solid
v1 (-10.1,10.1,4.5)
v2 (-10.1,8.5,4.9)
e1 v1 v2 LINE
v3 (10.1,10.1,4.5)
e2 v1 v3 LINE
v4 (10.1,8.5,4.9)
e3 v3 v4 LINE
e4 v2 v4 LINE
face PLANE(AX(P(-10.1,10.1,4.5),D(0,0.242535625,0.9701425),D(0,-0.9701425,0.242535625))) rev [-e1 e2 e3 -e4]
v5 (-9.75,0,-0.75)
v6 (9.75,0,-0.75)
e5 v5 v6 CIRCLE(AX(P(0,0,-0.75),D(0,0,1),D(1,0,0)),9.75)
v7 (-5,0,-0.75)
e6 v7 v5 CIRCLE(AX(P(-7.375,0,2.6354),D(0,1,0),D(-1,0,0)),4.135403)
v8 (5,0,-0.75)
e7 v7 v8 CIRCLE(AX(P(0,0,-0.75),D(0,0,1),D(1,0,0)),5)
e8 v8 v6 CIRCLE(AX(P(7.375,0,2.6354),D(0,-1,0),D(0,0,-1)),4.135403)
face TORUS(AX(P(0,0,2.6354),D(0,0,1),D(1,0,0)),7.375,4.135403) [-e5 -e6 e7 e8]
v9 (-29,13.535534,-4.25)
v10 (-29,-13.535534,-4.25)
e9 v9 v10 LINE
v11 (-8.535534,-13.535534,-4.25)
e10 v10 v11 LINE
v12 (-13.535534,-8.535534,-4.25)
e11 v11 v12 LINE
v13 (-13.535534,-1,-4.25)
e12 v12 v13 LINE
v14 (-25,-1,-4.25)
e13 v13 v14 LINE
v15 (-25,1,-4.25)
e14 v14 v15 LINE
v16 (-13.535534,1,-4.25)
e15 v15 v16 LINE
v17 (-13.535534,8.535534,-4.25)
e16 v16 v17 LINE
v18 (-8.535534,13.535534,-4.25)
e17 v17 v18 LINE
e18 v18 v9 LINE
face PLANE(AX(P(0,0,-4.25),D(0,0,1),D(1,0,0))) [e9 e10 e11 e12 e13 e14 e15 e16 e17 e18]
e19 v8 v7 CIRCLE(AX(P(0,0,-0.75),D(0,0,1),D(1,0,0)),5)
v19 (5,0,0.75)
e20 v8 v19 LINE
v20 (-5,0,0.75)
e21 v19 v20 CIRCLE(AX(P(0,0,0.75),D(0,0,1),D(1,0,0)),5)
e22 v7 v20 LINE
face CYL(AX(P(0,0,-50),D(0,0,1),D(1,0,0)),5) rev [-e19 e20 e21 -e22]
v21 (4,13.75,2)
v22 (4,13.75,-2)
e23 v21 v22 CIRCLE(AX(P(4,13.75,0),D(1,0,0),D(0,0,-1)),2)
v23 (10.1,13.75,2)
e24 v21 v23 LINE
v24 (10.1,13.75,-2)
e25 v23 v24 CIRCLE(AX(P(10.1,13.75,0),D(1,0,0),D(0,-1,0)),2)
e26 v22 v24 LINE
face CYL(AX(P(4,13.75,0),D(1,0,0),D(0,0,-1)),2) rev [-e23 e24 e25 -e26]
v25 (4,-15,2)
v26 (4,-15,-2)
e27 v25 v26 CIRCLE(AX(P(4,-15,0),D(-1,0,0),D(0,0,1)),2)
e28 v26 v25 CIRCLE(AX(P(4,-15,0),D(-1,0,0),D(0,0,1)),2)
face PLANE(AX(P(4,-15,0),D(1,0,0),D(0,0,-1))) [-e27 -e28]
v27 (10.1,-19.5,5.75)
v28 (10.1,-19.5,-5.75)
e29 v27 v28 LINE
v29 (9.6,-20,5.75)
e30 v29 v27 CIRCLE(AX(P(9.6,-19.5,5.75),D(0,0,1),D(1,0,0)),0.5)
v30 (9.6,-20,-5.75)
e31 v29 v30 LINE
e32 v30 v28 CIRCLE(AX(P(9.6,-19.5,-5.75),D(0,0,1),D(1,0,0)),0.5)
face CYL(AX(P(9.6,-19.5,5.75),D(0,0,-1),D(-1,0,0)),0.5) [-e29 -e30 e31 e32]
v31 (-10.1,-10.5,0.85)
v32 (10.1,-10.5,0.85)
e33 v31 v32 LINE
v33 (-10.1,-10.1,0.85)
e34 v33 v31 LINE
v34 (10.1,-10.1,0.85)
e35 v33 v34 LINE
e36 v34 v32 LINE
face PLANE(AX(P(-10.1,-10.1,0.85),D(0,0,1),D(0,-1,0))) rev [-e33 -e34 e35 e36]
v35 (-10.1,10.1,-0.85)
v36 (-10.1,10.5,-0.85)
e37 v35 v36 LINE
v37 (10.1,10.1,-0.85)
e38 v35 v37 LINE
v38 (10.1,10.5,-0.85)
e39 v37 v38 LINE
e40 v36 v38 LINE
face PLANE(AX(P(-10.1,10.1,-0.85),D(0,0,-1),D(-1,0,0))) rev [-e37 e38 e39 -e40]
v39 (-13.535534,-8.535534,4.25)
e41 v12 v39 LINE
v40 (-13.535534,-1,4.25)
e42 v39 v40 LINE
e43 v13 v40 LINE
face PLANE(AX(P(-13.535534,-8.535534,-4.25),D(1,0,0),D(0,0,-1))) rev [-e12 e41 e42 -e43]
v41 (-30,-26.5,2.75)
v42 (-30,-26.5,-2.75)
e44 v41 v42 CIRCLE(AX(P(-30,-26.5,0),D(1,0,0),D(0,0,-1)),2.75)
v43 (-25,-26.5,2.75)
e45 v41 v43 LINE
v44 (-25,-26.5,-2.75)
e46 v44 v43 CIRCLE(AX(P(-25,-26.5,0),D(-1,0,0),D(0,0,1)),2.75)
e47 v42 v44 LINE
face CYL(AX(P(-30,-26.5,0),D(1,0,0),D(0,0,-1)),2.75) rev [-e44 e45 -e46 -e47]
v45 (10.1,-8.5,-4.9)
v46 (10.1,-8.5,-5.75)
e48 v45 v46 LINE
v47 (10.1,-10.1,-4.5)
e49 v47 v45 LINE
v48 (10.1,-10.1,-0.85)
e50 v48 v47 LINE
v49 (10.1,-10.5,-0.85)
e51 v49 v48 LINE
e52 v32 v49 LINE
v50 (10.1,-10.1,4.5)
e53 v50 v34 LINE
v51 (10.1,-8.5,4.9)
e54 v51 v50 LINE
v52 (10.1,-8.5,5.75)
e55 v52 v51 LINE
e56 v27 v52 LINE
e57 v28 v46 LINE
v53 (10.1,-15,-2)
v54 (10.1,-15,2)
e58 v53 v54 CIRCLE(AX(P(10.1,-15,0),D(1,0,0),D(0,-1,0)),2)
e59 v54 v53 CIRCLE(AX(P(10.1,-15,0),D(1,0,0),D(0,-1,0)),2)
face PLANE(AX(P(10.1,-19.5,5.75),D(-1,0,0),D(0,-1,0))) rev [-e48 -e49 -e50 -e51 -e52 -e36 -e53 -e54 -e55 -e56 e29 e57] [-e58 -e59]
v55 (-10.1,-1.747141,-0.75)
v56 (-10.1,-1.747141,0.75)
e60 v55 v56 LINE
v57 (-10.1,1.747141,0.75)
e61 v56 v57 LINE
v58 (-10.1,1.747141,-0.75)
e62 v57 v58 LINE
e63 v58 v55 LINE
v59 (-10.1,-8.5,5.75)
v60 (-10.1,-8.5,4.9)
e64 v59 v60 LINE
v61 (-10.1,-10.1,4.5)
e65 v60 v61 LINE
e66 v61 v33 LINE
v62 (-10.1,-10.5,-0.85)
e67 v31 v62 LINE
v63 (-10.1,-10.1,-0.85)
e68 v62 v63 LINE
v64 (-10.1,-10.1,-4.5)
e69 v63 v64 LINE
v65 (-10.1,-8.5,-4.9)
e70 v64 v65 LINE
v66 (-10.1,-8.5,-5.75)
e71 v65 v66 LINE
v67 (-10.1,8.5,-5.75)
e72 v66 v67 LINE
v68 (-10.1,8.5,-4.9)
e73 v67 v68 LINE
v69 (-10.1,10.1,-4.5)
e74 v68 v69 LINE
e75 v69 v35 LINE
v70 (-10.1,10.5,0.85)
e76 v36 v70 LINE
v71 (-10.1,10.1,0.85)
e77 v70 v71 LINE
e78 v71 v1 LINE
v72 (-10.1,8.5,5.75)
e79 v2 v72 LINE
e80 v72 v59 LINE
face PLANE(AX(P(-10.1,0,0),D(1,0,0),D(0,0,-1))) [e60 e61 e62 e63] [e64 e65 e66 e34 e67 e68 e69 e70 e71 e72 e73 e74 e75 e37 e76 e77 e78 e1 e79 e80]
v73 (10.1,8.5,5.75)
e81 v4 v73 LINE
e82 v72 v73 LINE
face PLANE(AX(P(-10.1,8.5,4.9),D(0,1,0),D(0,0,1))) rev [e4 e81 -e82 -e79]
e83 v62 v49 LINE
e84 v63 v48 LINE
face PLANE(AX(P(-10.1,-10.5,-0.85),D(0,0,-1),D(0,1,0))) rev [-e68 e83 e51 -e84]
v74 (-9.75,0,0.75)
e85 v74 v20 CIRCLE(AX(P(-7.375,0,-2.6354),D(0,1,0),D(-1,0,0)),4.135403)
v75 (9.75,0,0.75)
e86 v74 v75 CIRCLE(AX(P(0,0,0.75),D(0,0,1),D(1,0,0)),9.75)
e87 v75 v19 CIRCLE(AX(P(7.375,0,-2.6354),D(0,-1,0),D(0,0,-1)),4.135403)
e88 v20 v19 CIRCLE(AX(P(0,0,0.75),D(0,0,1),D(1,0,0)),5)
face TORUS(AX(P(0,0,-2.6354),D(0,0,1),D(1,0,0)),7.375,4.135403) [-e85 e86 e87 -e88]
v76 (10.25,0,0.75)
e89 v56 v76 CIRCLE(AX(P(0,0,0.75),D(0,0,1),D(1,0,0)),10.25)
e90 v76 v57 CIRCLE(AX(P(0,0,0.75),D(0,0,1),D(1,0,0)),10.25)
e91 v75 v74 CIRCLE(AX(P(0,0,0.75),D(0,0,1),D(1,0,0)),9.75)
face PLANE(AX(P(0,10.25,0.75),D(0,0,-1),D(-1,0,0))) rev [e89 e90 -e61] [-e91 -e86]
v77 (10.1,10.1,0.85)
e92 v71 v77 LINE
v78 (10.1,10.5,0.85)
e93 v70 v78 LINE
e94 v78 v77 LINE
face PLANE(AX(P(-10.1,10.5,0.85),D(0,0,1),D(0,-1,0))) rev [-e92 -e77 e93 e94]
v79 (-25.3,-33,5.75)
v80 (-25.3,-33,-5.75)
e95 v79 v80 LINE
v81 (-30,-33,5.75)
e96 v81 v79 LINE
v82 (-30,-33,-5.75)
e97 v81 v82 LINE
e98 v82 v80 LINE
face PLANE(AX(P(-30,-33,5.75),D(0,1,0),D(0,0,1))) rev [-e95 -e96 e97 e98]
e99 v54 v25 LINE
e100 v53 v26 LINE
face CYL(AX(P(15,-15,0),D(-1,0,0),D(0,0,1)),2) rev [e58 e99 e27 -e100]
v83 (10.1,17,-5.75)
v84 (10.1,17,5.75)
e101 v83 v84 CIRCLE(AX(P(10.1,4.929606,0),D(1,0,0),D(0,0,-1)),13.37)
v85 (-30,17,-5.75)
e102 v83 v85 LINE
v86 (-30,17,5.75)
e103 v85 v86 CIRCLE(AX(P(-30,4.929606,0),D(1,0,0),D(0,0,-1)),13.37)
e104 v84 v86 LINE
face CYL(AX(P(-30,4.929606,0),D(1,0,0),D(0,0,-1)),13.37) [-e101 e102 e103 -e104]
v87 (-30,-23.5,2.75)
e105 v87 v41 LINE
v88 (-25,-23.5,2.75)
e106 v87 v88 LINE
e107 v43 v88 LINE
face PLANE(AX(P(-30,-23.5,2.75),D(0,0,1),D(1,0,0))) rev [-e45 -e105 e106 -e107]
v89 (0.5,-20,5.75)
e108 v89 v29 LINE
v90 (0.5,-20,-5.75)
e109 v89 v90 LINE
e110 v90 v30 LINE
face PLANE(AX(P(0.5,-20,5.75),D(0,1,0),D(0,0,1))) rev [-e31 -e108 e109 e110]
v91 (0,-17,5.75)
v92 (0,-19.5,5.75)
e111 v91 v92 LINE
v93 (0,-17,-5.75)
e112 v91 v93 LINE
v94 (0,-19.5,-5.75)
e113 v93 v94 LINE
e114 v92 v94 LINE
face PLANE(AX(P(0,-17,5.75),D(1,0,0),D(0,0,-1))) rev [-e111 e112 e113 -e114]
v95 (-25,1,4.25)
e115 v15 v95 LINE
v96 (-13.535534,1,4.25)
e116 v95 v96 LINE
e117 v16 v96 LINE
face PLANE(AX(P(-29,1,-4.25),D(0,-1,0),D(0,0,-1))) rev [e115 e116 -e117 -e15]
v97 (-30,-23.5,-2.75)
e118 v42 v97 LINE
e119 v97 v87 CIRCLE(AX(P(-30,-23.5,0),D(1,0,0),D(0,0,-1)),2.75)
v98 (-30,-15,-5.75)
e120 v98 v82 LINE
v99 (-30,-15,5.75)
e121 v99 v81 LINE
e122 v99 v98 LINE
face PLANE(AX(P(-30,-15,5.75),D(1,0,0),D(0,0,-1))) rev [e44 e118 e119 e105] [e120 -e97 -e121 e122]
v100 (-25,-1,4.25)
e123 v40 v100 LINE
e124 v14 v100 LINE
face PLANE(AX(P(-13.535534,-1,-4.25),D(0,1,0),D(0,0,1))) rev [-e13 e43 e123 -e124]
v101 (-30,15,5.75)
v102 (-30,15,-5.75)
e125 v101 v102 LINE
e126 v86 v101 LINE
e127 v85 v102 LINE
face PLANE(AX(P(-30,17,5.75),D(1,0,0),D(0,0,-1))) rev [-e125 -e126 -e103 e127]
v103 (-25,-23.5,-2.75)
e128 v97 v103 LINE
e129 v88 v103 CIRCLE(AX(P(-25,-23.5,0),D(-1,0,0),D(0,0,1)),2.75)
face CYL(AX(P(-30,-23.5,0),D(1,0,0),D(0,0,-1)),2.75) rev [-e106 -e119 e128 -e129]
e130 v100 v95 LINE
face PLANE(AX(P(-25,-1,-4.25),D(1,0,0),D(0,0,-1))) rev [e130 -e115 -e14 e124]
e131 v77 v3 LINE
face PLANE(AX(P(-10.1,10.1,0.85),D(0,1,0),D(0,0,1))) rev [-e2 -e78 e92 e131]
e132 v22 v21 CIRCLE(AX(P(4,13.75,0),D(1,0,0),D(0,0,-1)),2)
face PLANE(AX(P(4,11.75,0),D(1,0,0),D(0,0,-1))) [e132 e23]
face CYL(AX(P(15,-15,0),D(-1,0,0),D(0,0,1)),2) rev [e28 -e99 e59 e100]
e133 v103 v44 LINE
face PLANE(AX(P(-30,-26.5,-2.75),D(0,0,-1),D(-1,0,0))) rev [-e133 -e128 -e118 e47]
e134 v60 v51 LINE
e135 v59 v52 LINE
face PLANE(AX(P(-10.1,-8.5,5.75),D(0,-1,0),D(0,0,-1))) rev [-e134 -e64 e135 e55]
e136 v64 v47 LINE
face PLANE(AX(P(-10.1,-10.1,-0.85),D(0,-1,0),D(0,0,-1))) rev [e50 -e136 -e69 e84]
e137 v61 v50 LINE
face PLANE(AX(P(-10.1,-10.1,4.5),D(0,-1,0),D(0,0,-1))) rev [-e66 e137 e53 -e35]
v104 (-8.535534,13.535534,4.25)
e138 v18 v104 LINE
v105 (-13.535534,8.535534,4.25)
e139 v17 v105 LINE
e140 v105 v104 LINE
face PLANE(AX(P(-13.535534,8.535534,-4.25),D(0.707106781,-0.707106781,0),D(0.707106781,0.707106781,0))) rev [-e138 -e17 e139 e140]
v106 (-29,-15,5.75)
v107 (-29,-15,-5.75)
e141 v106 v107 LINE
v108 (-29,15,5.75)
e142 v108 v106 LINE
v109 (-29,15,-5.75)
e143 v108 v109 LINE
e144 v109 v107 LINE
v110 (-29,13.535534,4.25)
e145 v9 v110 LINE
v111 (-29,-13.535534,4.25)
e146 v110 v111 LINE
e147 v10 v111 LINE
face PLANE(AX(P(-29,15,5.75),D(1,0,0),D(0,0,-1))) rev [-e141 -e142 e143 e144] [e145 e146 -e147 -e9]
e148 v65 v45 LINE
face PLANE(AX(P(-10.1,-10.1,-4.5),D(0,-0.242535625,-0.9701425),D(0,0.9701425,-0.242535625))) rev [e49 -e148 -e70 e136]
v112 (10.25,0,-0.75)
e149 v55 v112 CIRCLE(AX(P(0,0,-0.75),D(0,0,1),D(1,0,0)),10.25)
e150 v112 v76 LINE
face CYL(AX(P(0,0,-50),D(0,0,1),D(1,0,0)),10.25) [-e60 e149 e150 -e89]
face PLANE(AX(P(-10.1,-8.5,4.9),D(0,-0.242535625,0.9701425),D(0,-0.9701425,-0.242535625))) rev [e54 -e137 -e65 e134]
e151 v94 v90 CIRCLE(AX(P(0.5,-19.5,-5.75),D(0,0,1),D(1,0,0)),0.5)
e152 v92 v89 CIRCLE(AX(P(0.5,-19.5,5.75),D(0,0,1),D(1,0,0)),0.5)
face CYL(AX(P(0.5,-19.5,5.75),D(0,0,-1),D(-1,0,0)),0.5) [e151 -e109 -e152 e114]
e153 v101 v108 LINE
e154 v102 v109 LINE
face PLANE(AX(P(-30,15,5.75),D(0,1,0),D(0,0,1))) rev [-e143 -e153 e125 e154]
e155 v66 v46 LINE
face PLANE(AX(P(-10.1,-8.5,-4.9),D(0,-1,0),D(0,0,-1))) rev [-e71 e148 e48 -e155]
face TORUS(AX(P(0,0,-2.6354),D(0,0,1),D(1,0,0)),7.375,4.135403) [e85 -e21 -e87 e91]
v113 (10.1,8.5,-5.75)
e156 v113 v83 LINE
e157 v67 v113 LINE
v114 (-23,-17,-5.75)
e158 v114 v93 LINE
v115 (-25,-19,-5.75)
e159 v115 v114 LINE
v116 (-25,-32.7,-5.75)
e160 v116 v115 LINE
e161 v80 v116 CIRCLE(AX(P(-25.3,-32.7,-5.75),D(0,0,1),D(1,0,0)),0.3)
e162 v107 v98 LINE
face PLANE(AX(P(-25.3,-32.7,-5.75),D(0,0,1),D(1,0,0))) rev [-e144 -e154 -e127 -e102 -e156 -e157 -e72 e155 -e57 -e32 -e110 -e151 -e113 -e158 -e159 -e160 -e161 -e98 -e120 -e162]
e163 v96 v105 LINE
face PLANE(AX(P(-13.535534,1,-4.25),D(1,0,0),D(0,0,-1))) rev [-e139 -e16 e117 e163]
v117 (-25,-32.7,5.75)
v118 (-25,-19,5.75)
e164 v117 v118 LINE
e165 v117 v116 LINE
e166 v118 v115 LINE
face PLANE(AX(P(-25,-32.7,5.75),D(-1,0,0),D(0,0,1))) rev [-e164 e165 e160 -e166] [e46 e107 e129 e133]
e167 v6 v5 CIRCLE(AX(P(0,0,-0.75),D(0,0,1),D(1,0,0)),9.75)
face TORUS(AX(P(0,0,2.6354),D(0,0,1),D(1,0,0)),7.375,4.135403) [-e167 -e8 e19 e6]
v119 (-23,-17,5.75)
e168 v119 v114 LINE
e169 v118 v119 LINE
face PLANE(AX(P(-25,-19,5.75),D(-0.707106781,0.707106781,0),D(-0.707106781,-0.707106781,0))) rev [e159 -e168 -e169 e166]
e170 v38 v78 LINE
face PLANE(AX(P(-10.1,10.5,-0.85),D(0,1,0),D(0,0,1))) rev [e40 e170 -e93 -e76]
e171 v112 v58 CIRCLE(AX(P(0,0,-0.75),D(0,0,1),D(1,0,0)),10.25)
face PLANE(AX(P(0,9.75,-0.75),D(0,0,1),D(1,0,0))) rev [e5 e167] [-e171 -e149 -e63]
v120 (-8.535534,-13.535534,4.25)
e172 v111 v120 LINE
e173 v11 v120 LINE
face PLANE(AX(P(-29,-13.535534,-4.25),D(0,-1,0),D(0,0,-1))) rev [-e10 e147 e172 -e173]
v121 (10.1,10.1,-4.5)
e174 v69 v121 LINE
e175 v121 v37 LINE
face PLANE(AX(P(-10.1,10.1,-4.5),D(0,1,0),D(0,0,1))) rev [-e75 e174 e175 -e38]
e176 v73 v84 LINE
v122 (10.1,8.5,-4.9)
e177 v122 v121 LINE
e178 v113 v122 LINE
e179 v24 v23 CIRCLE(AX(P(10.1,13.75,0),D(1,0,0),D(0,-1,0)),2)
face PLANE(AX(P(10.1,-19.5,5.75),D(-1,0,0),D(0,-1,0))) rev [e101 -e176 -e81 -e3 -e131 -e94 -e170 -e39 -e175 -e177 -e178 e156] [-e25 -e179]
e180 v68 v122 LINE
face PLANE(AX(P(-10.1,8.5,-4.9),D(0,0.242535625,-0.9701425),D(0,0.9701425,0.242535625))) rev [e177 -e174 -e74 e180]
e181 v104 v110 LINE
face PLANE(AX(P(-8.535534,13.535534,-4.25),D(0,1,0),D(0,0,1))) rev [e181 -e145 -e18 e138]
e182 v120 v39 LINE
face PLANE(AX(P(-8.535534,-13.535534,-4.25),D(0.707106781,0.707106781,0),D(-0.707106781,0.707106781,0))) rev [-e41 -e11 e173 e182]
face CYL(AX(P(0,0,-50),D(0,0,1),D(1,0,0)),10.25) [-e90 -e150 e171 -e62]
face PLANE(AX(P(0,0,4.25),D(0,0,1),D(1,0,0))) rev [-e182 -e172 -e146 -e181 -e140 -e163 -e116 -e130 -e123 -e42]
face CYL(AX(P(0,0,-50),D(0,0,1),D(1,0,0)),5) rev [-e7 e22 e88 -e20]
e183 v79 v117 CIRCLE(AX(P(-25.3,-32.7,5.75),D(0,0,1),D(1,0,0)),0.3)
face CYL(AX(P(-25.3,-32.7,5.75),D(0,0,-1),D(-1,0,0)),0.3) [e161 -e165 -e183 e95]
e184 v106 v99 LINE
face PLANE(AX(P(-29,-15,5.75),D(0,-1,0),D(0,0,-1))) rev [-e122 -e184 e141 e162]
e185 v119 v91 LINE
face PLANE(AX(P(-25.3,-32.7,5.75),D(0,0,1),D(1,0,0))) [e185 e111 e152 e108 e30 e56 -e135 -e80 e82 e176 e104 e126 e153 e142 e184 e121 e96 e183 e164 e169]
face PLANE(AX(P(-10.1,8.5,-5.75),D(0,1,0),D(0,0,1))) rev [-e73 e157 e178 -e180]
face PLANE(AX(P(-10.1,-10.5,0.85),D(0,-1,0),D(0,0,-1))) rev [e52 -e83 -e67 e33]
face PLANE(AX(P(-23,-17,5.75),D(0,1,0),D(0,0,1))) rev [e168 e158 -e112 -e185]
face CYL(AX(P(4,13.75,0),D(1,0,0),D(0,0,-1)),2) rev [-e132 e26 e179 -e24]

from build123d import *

# Parameters (mm, degrees)
EXTRUDE_1_DEPTH          = 5.75
EXTRUDE_1_DEPTH_BACK     = 5.75
CUT_EXTRUDE_1_DEPTH      = 30
EXTRUDE_2_DEPTH          = 40.1
CUT_EXTRUDE_2_DEPTH      = 20.2
CUT_EXTRUDE_3_DEPTH      = 4.25
CUT_EXTRUDE_3_DEPTH_BACK = 4.25
CUT_EXTRUDE_4_DEPTH      = 4.25
CUT_EXTRUDE_4_DEPTH_BACK = 4.25
CUT_EXTRUDE_5_DEPTH      = 4.25
CUT_EXTRUDE_5_DEPTH_BACK = 4.25
SKETCH_10_W              = 4
SKETCH_10_H              = 2


with BuildPart() as part:
    # 草图1 → 凸台-拉伸1 (new, two sides: drawn at the far end of the back side and taken through both)
    with BuildSketch(Plane.XY.offset(-EXTRUDE_1_DEPTH_BACK)):
        with BuildLine():
            Line((-30, 17), (-30, 15))
            Line((-30, 15), (-29, 15))
            Line((-29, 15), (-29, -15))
            Line((-29, -15), (-30, -15))
            Line((-30, -15), (-30, -33))
            Line((-30, -33), (-25.3, -33))
            ThreePointArc((-25.3, -33), (-25.087867966, -32.912132034), (-25, -32.7))
            Line((-25, -32.7), (-25, -19))
            Line((-25, -19), (-23, -17))
            Line((-23, -17), (0, -17))
            Line((0, -17), (0, -19.5))
            ThreePointArc((0, -19.5), (0.146446609, -19.853553391), (0.5, -20))
            Line((0.5, -20), (9.6, -20))
            ThreePointArc((9.6, -20), (9.953553391, -19.853553391), (10.1, -19.5))
            Line((10.1, -19.5), (10.1, 17))
            Line((10.1, 17), (-30, 17))
        make_face()
    extrude(amount=EXTRUDE_1_DEPTH + EXTRUDE_1_DEPTH_BACK)

    # 草图2 → 切除-拉伸1 (cut)
    with BuildSketch(Plane(origin=(0, 0, 0), x_dir=(0, 0, -1), z_dir=(1, 0, 0))):
        with BuildLine():
            Line((-2.75, -23.5), (-2.75, -26.5))
            ThreePointArc((-2.75, -26.5), (0, -29.25), (2.75, -26.5))
            Line((2.75, -26.5), (2.75, -23.5))
            ThreePointArc((2.75, -23.5), (0, -20.75), (-2.75, -23.5))
        make_face()
    extrude(amount=-CUT_EXTRUDE_1_DEPTH, mode=Mode.SUBTRACT)

    # 草图3 → 凸台-拉伸2 (add)
    with BuildSketch(Plane(origin=(10.1, 0, 0), x_dir=(0, 0, -1), z_dir=(1, 0, 0))):
        with BuildLine():
            Line((-5.75, 17), (5.75, 17))
            ThreePointArc((5.75, 17), (0, 18.299606469), (-5.75, 17))
        make_face()
    extrude(amount=-EXTRUDE_2_DEPTH)

    # 草图4 → 切除-旋转1 (revolve, cut)
    with BuildSketch(Plane.XY, mode=Mode.PRIVATE) as cut_revolve_1_sk:
        Polygon((4, -15), (4, -13), (11, -13), (11, -11.25), (14.5, -11.25), (15, -10.75), (15, -15), align=None)
    revolve(cut_revolve_1_sk.sketch.rotate(Axis((15, -15, 0), (-1, 0, 0)), 270), axis=Axis((15, -15, 0), (-1, 0, 0)), mode=Mode.SUBTRACT)

    # 草图5 → 切除-旋转2 (revolve, cut)
    with BuildSketch(Plane.XY, mode=Mode.PRIVATE) as cut_revolve_2_sk:
        Polygon((15, 13.75), (15, 9.5), (14.5, 10), (11, 10), (11, 11.75), (4, 11.75), (4, 13.75), align=None)
    revolve(cut_revolve_2_sk.sketch.rotate(Axis((4, 13.75, 0), (1, 0, 0)), 90), axis=Axis((4, 13.75, 0), (1, 0, 0)), mode=Mode.SUBTRACT)

    # 草图6 → 切除-拉伸2 (cut)
    with BuildSketch(Plane(origin=(10.1, 0, 0), x_dir=(0, 0, -1), z_dir=(1, 0, 0))):
        Polygon((-5.75, -8.5), (-4.9, -8.5), (-4.5, -10.1), (-0.85, -10.1), (-0.85, -10.5), (0.85, -10.5), (0.85, -10.1), (4.5, -10.1), (4.9, -8.5), (5.75, -8.5), (5.75, 8.5), (4.9, 8.5), (4.5, 10.1), (0.85, 10.1), (0.85, 10.5), (-0.85, 10.5), (-0.85, 10.1), (-4.5, 10.1), (-4.9, 8.5), (-5.75, 8.5), align=None)
    extrude(amount=-CUT_EXTRUDE_2_DEPTH, mode=Mode.SUBTRACT)

    # 草图7 → 旋转1 (revolve)
    with BuildSketch(Plane(origin=(0, 0, 0), x_dir=(0, 0, -1), z_dir=(1, 0, 0)), mode=Mode.PRIVATE) as revolve_1_sk:
        with BuildLine():
            Line((-0.75, 5), (0.75, 5))
            ThreePointArc((0.75, 5), (1.500003023, 7.375), (0.75, 9.75))
            Line((0.75, 9.75), (0.75, 10.25))
            Line((0.75, 10.25), (-0.75, 10.25))
            Line((-0.75, 10.25), (-0.75, 9.75))
            ThreePointArc((-0.75, 9.75), (-1.500003023, 7.375), (-0.75, 5))
        make_face()
    revolve(revolve_1_sk.sketch.rotate(Axis((0, 0, -50), (0, 0, 1)), 270), axis=Axis((0, 0, -50), (0, 0, 1)))

    # 草图8 → 切除-拉伸3 (cut, two sides: drawn at the far end of the back side and taken through both)
    with BuildSketch(Plane.XY.offset(-CUT_EXTRUDE_3_DEPTH_BACK)):
        Polygon((-29, 13.535533906), (-29, 1), (-13.535533906, 1), (-13.535533906, 8.535533906), (-8.535533906, 13.535533906), align=None)
    extrude(amount=CUT_EXTRUDE_3_DEPTH + CUT_EXTRUDE_3_DEPTH_BACK, mode=Mode.SUBTRACT)

    # 草图9 → 切除-拉伸4 (cut, two sides: drawn at the far end of the back side and taken through both)
    with BuildSketch(Plane.XY.offset(-CUT_EXTRUDE_4_DEPTH_BACK)):
        Polygon((-29, -13.535533906), (-8.535533906, -13.535533906), (-13.535533906, -8.535533906), (-13.535533906, -1), (-29, -1), align=None)
    extrude(amount=CUT_EXTRUDE_4_DEPTH + CUT_EXTRUDE_4_DEPTH_BACK, mode=Mode.SUBTRACT)

    # 草图10 → 切除-拉伸5 (cut, two sides: drawn at the far end of the back side and taken through both)
    with BuildSketch(Plane.XY.offset(-CUT_EXTRUDE_5_DEPTH_BACK)):
        with Locations((-27, 0)):
            Rectangle(SKETCH_10_W, SKETCH_10_H)
    extrude(amount=CUT_EXTRUDE_5_DEPTH + CUT_EXTRUDE_5_DEPTH_BACK, mode=Mode.SUBTRACT)


solid = part.part
